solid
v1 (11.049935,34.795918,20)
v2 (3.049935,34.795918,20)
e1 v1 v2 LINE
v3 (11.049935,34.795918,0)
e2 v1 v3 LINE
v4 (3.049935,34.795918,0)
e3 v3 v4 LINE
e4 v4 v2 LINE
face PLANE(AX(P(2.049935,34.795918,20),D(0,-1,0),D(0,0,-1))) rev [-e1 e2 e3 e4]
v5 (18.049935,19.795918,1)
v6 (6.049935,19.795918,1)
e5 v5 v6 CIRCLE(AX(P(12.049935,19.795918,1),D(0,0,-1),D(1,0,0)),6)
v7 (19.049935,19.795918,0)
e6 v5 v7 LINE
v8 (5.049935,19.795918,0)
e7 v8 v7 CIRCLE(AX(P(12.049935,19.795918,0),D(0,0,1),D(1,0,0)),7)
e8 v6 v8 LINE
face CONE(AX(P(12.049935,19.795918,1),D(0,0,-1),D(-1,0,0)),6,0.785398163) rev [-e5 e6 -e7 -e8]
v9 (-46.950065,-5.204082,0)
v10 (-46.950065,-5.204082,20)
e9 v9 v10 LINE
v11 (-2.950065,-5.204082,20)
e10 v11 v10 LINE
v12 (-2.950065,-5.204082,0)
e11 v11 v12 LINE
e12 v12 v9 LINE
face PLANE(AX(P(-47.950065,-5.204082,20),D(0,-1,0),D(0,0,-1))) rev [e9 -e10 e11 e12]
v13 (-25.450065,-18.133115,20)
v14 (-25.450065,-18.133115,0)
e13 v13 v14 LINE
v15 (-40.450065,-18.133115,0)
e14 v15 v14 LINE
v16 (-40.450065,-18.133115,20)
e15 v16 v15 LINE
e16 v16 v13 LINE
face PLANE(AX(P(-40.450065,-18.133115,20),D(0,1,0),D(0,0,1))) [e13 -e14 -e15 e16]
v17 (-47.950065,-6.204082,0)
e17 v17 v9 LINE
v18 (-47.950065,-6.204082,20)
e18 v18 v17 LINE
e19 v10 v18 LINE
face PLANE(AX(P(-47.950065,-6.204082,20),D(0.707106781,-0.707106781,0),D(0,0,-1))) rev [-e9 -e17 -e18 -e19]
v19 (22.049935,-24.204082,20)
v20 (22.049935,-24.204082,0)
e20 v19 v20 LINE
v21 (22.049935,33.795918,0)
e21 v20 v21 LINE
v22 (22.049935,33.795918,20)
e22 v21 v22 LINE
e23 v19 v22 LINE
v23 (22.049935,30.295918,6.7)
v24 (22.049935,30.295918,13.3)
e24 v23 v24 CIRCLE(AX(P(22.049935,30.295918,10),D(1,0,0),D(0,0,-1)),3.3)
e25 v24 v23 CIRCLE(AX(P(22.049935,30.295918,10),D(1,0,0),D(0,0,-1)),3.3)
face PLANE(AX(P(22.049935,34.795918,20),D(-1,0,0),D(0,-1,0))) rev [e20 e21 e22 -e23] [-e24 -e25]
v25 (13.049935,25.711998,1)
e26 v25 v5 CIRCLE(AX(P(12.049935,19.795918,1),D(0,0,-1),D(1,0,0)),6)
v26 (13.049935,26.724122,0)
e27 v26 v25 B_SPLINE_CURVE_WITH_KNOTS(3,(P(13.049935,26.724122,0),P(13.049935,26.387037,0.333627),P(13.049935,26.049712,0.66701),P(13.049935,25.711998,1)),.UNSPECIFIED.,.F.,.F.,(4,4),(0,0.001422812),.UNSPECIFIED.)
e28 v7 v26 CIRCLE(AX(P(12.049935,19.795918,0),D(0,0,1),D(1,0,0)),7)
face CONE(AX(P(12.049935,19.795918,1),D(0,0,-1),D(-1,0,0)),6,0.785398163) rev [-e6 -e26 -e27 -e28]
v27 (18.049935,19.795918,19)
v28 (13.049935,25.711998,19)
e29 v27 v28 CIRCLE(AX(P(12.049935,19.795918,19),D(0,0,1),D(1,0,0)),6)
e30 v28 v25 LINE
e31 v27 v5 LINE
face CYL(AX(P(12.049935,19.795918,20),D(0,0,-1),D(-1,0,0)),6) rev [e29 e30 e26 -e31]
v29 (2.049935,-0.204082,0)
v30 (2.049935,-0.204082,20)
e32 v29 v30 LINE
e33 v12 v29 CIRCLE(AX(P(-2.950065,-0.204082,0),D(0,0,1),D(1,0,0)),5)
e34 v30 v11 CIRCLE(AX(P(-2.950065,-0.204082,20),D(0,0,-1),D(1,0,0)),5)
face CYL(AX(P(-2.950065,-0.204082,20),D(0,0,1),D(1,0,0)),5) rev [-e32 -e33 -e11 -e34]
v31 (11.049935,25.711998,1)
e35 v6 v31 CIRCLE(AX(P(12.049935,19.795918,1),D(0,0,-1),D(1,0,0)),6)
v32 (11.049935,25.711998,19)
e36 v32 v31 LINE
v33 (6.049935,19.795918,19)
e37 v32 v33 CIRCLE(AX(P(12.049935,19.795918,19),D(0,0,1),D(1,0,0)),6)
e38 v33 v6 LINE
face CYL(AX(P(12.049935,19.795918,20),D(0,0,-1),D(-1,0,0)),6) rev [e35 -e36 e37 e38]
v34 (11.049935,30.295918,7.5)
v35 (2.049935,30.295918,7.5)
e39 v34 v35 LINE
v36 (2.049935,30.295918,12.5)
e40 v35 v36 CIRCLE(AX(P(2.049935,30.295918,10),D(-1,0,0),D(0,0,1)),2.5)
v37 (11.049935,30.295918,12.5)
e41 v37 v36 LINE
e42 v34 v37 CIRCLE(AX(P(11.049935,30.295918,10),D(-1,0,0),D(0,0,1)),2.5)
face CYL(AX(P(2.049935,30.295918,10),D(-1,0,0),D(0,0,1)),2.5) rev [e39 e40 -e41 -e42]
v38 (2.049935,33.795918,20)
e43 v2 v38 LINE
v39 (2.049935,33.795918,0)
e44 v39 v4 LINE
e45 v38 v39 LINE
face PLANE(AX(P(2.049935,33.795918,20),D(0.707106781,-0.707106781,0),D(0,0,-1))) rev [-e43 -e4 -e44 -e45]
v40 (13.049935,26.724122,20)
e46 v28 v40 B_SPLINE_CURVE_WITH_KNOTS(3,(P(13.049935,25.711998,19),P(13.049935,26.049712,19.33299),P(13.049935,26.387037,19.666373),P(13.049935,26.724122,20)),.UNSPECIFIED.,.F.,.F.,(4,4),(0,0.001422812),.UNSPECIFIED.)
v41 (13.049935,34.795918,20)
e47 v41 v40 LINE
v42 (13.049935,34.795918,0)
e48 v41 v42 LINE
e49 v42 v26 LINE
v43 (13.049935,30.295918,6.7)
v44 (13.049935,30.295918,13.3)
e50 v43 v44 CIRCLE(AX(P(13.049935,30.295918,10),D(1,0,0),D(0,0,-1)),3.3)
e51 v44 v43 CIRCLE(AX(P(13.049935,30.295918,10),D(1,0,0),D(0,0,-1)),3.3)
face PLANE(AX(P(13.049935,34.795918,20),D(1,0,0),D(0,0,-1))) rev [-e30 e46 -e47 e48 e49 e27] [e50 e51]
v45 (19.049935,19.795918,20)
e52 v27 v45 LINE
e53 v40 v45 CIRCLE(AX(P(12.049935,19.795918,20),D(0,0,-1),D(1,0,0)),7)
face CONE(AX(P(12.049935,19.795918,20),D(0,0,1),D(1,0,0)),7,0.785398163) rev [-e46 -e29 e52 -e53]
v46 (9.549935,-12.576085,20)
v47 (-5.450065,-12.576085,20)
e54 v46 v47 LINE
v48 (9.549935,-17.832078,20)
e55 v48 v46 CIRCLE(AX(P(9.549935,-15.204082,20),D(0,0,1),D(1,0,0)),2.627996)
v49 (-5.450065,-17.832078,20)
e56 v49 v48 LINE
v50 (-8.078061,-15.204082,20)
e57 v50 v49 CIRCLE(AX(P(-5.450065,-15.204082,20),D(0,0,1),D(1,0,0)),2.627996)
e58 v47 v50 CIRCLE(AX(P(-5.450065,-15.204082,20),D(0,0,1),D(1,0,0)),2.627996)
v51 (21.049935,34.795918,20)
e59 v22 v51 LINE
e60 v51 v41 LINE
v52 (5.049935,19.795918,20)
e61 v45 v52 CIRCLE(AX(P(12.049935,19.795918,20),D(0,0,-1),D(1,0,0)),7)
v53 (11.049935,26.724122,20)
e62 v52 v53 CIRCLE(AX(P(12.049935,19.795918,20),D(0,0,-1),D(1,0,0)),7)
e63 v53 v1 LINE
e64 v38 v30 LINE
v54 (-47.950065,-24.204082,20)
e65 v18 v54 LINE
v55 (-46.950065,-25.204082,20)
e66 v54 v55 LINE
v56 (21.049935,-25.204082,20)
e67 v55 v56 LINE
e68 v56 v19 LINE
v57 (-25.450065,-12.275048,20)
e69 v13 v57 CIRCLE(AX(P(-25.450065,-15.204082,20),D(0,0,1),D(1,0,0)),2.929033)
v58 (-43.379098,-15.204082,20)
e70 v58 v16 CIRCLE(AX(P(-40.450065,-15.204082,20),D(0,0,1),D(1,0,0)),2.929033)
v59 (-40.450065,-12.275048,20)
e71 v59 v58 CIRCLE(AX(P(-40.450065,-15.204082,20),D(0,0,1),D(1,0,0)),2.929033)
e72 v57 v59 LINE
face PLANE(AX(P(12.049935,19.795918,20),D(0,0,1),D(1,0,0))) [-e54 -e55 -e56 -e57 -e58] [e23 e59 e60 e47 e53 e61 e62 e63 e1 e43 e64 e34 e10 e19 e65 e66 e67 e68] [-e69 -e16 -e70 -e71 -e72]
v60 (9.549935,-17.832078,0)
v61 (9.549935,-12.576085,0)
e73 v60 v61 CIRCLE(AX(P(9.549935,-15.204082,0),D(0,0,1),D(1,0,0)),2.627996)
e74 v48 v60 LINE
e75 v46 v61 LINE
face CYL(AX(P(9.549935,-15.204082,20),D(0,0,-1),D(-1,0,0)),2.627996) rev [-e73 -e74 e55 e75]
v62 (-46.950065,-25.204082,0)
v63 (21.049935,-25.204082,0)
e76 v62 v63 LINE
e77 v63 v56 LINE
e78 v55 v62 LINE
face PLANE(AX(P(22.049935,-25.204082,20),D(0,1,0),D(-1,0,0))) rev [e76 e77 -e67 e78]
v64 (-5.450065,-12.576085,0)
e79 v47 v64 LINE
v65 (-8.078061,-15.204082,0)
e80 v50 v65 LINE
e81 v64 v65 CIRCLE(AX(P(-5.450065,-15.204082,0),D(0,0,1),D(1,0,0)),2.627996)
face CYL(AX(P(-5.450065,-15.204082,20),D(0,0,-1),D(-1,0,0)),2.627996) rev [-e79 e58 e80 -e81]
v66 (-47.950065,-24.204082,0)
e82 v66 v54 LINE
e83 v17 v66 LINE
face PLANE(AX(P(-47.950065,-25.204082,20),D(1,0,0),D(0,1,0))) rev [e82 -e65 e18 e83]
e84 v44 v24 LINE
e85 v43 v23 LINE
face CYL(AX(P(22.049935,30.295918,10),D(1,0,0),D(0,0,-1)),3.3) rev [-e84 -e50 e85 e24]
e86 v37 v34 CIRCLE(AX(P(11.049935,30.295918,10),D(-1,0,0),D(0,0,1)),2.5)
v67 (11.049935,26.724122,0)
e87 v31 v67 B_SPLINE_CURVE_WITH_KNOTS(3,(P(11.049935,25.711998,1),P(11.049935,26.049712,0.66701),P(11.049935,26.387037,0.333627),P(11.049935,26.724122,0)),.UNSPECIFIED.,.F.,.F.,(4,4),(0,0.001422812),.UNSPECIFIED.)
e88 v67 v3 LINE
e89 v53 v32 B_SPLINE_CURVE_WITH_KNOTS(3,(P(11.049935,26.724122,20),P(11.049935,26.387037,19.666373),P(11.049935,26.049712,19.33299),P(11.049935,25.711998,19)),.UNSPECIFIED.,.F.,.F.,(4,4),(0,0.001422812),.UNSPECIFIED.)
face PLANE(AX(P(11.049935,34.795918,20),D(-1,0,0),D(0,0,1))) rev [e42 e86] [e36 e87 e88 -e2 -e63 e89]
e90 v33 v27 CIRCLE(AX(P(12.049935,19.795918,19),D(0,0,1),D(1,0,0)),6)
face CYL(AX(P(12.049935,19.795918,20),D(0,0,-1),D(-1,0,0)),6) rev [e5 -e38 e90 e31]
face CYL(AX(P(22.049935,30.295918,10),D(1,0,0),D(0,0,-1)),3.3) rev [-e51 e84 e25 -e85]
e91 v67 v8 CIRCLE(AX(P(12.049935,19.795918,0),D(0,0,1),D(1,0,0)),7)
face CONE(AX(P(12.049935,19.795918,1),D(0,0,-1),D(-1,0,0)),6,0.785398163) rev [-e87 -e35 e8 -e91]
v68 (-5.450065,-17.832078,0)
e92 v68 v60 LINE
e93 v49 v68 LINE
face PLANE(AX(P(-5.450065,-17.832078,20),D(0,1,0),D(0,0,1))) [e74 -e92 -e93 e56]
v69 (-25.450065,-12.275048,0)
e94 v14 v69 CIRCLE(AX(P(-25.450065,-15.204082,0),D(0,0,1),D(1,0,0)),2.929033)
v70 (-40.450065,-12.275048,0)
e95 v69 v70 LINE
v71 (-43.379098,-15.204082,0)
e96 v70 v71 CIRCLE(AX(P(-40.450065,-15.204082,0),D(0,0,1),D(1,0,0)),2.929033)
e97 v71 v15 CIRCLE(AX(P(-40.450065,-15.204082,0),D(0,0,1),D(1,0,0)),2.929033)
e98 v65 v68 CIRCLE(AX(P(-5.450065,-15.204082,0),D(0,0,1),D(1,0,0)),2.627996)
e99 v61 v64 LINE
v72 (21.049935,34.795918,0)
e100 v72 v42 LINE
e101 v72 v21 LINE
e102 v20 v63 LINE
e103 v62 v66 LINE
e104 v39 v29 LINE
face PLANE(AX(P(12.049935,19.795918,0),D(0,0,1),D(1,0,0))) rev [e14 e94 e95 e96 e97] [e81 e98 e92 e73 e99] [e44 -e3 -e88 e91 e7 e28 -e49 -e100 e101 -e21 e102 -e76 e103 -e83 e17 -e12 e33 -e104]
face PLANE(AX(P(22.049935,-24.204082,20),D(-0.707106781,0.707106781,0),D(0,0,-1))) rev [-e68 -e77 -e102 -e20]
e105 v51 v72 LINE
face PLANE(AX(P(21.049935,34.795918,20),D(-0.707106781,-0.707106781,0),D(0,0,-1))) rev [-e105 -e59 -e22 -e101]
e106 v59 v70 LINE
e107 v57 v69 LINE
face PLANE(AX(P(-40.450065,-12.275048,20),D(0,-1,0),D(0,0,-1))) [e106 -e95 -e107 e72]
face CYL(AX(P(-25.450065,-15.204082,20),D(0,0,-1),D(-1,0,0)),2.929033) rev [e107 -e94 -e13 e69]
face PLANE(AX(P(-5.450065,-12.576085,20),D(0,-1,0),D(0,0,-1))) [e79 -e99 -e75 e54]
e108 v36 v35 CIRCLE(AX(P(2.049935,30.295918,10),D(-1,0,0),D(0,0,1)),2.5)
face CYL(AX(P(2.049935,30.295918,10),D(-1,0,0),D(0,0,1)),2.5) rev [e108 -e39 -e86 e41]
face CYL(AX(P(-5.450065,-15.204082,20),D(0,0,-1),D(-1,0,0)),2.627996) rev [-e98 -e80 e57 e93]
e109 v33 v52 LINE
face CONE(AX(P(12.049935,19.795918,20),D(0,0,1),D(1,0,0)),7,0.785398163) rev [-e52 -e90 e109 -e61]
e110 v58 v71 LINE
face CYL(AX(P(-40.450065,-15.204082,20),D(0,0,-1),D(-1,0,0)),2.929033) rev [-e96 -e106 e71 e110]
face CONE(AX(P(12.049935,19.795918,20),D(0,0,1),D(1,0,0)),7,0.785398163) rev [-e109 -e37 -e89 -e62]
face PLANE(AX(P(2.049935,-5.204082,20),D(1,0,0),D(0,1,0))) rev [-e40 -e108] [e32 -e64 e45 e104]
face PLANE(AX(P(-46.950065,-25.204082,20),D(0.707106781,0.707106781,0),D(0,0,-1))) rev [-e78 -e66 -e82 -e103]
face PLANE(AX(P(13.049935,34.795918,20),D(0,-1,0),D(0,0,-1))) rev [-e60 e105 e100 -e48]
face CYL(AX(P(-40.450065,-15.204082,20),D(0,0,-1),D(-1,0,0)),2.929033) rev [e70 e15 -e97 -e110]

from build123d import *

# Parameters (mm, degrees)
BOSS_EXTRUDE1_DEPTH   = 20
CHAMFER1_SIZE         = 1
M6_TAPPED_HOLE1_D     = 5
M6_TAPPED_HOLE1_DEPTH = 9
M6_TAPPED_HOLE1_TIP   = 1.502151548
HOLE1_D               = 6.6
HOLE1_DEPTH           = 9
CHAMFER2_SIZE         = 1
FILLET1_R             = 5


with BuildPart() as part:
    # Sketch1 → Boss-Extrude1 (new body)
    with BuildSketch(Plane.XY):
        with BuildLine():
            Line((22.049935288, 34.795918367), (22.049935288, -25.204081633))
            Line((22.049935288, -25.204081633), (-47.950064712, -25.204081633))
            Line((-47.950064712, -25.204081633), (-47.950064712, -5.204081633))
            Line((-47.950064712, -5.204081633), (2.049935288, -5.204081633))
            Line((2.049935288, -5.204081633), (2.049935288, 34.795918367))
            Line((2.049935288, 34.795918367), (11.049935288, 34.795918367))
            Line((11.049935288, 34.795918367), (11.049935288, 25.71199815))
            ThreePointArc((11.049935288, 25.71199815), (12.049935288, 13.795918367), (13.049935288, 25.71199815))
            Line((13.049935288, 25.71199815), (13.049935288, 34.795918367))
            Line((13.049935288, 34.795918367), (22.049935288, 34.795918367))
        make_face()
        with BuildLine():
            Line((-40.450064712, -12.275048454), (-25.450064712, -12.275048454))
            ThreePointArc((-25.450064712, -12.275048454), (-22.521031533, -15.204081633), (-25.450064712, -18.133114812))
            Line((-25.450064712, -18.133114812), (-40.450064712, -18.133114812))
            ThreePointArc((-40.450064712, -18.133114812), (-43.379097891, -15.204081633), (-40.450064712, -12.275048454))
        make_face(mode=Mode.SUBTRACT)
        with BuildLine():
            Line((-5.450064712, -12.576085385), (9.549935288, -12.576085385))
            ThreePointArc((9.549935288, -12.576085385), (12.177931536, -15.204081633), (9.549935288, -17.832077881))
            Line((9.549935288, -17.832077881), (-5.450064712, -17.832077881))
            ThreePointArc((-5.450064712, -17.832077881), (-8.07806096, -15.204081633), (-5.450064712, -12.576085385))
        make_face(mode=Mode.SUBTRACT)
    extrude(amount=BOSS_EXTRUDE1_DEPTH)

    # Chamfer1
    chamfer1_edges = [part.edges().sort_by_distance(p)[0] for p in [
        (12.049935288, 13.795918367, 20),
        (12.049935288, 13.795918367, 0),
    ]]
    chamfer(chamfer1_edges, length=CHAMFER1_SIZE)

    # M6 Tapped Hole1
    with Locations(Plane.ZY.offset(-2.049935288)):
        with Locations((10, 30.295918367)):
            Hole(M6_TAPPED_HOLE1_D / 2, depth=M6_TAPPED_HOLE1_DEPTH)
            with Locations((0, 0, -(M6_TAPPED_HOLE1_DEPTH + M6_TAPPED_HOLE1_TIP / 2))):  # 118° drill point
                Cone(0, M6_TAPPED_HOLE1_D / 2, M6_TAPPED_HOLE1_TIP, mode=Mode.SUBTRACT)

    # Hole1
    with Locations(Plane(origin=(22.049935288, 0, 0), x_dir=(0, 0, -1), z_dir=(1, 0, 0))):
        with Locations((-10, 30.295918367)):
            Hole(HOLE1_D / 2, depth=HOLE1_DEPTH)

    # Chamfer2
    chamfer2_edges = [part.edges().sort_by_distance(p)[0] for p in [
        (22.049935288, 34.795918367, 10),
        (22.049935288, -25.204081633, 10),
        (-47.950064712, -25.204081633, 10),
        (-47.950064712, -5.204081633, 10),
        (2.049935288, 34.795918367, 10),
    ]]
    chamfer(chamfer2_edges, length=CHAMFER2_SIZE)

    # Fillet1
    fillet1_edges = [part.edges().sort_by_distance(p)[0] for p in [
        (2.049935288, -5.204081633, 10),
    ]]
    fillet(fillet1_edges, radius=FILLET1_R)


solid = part.part
